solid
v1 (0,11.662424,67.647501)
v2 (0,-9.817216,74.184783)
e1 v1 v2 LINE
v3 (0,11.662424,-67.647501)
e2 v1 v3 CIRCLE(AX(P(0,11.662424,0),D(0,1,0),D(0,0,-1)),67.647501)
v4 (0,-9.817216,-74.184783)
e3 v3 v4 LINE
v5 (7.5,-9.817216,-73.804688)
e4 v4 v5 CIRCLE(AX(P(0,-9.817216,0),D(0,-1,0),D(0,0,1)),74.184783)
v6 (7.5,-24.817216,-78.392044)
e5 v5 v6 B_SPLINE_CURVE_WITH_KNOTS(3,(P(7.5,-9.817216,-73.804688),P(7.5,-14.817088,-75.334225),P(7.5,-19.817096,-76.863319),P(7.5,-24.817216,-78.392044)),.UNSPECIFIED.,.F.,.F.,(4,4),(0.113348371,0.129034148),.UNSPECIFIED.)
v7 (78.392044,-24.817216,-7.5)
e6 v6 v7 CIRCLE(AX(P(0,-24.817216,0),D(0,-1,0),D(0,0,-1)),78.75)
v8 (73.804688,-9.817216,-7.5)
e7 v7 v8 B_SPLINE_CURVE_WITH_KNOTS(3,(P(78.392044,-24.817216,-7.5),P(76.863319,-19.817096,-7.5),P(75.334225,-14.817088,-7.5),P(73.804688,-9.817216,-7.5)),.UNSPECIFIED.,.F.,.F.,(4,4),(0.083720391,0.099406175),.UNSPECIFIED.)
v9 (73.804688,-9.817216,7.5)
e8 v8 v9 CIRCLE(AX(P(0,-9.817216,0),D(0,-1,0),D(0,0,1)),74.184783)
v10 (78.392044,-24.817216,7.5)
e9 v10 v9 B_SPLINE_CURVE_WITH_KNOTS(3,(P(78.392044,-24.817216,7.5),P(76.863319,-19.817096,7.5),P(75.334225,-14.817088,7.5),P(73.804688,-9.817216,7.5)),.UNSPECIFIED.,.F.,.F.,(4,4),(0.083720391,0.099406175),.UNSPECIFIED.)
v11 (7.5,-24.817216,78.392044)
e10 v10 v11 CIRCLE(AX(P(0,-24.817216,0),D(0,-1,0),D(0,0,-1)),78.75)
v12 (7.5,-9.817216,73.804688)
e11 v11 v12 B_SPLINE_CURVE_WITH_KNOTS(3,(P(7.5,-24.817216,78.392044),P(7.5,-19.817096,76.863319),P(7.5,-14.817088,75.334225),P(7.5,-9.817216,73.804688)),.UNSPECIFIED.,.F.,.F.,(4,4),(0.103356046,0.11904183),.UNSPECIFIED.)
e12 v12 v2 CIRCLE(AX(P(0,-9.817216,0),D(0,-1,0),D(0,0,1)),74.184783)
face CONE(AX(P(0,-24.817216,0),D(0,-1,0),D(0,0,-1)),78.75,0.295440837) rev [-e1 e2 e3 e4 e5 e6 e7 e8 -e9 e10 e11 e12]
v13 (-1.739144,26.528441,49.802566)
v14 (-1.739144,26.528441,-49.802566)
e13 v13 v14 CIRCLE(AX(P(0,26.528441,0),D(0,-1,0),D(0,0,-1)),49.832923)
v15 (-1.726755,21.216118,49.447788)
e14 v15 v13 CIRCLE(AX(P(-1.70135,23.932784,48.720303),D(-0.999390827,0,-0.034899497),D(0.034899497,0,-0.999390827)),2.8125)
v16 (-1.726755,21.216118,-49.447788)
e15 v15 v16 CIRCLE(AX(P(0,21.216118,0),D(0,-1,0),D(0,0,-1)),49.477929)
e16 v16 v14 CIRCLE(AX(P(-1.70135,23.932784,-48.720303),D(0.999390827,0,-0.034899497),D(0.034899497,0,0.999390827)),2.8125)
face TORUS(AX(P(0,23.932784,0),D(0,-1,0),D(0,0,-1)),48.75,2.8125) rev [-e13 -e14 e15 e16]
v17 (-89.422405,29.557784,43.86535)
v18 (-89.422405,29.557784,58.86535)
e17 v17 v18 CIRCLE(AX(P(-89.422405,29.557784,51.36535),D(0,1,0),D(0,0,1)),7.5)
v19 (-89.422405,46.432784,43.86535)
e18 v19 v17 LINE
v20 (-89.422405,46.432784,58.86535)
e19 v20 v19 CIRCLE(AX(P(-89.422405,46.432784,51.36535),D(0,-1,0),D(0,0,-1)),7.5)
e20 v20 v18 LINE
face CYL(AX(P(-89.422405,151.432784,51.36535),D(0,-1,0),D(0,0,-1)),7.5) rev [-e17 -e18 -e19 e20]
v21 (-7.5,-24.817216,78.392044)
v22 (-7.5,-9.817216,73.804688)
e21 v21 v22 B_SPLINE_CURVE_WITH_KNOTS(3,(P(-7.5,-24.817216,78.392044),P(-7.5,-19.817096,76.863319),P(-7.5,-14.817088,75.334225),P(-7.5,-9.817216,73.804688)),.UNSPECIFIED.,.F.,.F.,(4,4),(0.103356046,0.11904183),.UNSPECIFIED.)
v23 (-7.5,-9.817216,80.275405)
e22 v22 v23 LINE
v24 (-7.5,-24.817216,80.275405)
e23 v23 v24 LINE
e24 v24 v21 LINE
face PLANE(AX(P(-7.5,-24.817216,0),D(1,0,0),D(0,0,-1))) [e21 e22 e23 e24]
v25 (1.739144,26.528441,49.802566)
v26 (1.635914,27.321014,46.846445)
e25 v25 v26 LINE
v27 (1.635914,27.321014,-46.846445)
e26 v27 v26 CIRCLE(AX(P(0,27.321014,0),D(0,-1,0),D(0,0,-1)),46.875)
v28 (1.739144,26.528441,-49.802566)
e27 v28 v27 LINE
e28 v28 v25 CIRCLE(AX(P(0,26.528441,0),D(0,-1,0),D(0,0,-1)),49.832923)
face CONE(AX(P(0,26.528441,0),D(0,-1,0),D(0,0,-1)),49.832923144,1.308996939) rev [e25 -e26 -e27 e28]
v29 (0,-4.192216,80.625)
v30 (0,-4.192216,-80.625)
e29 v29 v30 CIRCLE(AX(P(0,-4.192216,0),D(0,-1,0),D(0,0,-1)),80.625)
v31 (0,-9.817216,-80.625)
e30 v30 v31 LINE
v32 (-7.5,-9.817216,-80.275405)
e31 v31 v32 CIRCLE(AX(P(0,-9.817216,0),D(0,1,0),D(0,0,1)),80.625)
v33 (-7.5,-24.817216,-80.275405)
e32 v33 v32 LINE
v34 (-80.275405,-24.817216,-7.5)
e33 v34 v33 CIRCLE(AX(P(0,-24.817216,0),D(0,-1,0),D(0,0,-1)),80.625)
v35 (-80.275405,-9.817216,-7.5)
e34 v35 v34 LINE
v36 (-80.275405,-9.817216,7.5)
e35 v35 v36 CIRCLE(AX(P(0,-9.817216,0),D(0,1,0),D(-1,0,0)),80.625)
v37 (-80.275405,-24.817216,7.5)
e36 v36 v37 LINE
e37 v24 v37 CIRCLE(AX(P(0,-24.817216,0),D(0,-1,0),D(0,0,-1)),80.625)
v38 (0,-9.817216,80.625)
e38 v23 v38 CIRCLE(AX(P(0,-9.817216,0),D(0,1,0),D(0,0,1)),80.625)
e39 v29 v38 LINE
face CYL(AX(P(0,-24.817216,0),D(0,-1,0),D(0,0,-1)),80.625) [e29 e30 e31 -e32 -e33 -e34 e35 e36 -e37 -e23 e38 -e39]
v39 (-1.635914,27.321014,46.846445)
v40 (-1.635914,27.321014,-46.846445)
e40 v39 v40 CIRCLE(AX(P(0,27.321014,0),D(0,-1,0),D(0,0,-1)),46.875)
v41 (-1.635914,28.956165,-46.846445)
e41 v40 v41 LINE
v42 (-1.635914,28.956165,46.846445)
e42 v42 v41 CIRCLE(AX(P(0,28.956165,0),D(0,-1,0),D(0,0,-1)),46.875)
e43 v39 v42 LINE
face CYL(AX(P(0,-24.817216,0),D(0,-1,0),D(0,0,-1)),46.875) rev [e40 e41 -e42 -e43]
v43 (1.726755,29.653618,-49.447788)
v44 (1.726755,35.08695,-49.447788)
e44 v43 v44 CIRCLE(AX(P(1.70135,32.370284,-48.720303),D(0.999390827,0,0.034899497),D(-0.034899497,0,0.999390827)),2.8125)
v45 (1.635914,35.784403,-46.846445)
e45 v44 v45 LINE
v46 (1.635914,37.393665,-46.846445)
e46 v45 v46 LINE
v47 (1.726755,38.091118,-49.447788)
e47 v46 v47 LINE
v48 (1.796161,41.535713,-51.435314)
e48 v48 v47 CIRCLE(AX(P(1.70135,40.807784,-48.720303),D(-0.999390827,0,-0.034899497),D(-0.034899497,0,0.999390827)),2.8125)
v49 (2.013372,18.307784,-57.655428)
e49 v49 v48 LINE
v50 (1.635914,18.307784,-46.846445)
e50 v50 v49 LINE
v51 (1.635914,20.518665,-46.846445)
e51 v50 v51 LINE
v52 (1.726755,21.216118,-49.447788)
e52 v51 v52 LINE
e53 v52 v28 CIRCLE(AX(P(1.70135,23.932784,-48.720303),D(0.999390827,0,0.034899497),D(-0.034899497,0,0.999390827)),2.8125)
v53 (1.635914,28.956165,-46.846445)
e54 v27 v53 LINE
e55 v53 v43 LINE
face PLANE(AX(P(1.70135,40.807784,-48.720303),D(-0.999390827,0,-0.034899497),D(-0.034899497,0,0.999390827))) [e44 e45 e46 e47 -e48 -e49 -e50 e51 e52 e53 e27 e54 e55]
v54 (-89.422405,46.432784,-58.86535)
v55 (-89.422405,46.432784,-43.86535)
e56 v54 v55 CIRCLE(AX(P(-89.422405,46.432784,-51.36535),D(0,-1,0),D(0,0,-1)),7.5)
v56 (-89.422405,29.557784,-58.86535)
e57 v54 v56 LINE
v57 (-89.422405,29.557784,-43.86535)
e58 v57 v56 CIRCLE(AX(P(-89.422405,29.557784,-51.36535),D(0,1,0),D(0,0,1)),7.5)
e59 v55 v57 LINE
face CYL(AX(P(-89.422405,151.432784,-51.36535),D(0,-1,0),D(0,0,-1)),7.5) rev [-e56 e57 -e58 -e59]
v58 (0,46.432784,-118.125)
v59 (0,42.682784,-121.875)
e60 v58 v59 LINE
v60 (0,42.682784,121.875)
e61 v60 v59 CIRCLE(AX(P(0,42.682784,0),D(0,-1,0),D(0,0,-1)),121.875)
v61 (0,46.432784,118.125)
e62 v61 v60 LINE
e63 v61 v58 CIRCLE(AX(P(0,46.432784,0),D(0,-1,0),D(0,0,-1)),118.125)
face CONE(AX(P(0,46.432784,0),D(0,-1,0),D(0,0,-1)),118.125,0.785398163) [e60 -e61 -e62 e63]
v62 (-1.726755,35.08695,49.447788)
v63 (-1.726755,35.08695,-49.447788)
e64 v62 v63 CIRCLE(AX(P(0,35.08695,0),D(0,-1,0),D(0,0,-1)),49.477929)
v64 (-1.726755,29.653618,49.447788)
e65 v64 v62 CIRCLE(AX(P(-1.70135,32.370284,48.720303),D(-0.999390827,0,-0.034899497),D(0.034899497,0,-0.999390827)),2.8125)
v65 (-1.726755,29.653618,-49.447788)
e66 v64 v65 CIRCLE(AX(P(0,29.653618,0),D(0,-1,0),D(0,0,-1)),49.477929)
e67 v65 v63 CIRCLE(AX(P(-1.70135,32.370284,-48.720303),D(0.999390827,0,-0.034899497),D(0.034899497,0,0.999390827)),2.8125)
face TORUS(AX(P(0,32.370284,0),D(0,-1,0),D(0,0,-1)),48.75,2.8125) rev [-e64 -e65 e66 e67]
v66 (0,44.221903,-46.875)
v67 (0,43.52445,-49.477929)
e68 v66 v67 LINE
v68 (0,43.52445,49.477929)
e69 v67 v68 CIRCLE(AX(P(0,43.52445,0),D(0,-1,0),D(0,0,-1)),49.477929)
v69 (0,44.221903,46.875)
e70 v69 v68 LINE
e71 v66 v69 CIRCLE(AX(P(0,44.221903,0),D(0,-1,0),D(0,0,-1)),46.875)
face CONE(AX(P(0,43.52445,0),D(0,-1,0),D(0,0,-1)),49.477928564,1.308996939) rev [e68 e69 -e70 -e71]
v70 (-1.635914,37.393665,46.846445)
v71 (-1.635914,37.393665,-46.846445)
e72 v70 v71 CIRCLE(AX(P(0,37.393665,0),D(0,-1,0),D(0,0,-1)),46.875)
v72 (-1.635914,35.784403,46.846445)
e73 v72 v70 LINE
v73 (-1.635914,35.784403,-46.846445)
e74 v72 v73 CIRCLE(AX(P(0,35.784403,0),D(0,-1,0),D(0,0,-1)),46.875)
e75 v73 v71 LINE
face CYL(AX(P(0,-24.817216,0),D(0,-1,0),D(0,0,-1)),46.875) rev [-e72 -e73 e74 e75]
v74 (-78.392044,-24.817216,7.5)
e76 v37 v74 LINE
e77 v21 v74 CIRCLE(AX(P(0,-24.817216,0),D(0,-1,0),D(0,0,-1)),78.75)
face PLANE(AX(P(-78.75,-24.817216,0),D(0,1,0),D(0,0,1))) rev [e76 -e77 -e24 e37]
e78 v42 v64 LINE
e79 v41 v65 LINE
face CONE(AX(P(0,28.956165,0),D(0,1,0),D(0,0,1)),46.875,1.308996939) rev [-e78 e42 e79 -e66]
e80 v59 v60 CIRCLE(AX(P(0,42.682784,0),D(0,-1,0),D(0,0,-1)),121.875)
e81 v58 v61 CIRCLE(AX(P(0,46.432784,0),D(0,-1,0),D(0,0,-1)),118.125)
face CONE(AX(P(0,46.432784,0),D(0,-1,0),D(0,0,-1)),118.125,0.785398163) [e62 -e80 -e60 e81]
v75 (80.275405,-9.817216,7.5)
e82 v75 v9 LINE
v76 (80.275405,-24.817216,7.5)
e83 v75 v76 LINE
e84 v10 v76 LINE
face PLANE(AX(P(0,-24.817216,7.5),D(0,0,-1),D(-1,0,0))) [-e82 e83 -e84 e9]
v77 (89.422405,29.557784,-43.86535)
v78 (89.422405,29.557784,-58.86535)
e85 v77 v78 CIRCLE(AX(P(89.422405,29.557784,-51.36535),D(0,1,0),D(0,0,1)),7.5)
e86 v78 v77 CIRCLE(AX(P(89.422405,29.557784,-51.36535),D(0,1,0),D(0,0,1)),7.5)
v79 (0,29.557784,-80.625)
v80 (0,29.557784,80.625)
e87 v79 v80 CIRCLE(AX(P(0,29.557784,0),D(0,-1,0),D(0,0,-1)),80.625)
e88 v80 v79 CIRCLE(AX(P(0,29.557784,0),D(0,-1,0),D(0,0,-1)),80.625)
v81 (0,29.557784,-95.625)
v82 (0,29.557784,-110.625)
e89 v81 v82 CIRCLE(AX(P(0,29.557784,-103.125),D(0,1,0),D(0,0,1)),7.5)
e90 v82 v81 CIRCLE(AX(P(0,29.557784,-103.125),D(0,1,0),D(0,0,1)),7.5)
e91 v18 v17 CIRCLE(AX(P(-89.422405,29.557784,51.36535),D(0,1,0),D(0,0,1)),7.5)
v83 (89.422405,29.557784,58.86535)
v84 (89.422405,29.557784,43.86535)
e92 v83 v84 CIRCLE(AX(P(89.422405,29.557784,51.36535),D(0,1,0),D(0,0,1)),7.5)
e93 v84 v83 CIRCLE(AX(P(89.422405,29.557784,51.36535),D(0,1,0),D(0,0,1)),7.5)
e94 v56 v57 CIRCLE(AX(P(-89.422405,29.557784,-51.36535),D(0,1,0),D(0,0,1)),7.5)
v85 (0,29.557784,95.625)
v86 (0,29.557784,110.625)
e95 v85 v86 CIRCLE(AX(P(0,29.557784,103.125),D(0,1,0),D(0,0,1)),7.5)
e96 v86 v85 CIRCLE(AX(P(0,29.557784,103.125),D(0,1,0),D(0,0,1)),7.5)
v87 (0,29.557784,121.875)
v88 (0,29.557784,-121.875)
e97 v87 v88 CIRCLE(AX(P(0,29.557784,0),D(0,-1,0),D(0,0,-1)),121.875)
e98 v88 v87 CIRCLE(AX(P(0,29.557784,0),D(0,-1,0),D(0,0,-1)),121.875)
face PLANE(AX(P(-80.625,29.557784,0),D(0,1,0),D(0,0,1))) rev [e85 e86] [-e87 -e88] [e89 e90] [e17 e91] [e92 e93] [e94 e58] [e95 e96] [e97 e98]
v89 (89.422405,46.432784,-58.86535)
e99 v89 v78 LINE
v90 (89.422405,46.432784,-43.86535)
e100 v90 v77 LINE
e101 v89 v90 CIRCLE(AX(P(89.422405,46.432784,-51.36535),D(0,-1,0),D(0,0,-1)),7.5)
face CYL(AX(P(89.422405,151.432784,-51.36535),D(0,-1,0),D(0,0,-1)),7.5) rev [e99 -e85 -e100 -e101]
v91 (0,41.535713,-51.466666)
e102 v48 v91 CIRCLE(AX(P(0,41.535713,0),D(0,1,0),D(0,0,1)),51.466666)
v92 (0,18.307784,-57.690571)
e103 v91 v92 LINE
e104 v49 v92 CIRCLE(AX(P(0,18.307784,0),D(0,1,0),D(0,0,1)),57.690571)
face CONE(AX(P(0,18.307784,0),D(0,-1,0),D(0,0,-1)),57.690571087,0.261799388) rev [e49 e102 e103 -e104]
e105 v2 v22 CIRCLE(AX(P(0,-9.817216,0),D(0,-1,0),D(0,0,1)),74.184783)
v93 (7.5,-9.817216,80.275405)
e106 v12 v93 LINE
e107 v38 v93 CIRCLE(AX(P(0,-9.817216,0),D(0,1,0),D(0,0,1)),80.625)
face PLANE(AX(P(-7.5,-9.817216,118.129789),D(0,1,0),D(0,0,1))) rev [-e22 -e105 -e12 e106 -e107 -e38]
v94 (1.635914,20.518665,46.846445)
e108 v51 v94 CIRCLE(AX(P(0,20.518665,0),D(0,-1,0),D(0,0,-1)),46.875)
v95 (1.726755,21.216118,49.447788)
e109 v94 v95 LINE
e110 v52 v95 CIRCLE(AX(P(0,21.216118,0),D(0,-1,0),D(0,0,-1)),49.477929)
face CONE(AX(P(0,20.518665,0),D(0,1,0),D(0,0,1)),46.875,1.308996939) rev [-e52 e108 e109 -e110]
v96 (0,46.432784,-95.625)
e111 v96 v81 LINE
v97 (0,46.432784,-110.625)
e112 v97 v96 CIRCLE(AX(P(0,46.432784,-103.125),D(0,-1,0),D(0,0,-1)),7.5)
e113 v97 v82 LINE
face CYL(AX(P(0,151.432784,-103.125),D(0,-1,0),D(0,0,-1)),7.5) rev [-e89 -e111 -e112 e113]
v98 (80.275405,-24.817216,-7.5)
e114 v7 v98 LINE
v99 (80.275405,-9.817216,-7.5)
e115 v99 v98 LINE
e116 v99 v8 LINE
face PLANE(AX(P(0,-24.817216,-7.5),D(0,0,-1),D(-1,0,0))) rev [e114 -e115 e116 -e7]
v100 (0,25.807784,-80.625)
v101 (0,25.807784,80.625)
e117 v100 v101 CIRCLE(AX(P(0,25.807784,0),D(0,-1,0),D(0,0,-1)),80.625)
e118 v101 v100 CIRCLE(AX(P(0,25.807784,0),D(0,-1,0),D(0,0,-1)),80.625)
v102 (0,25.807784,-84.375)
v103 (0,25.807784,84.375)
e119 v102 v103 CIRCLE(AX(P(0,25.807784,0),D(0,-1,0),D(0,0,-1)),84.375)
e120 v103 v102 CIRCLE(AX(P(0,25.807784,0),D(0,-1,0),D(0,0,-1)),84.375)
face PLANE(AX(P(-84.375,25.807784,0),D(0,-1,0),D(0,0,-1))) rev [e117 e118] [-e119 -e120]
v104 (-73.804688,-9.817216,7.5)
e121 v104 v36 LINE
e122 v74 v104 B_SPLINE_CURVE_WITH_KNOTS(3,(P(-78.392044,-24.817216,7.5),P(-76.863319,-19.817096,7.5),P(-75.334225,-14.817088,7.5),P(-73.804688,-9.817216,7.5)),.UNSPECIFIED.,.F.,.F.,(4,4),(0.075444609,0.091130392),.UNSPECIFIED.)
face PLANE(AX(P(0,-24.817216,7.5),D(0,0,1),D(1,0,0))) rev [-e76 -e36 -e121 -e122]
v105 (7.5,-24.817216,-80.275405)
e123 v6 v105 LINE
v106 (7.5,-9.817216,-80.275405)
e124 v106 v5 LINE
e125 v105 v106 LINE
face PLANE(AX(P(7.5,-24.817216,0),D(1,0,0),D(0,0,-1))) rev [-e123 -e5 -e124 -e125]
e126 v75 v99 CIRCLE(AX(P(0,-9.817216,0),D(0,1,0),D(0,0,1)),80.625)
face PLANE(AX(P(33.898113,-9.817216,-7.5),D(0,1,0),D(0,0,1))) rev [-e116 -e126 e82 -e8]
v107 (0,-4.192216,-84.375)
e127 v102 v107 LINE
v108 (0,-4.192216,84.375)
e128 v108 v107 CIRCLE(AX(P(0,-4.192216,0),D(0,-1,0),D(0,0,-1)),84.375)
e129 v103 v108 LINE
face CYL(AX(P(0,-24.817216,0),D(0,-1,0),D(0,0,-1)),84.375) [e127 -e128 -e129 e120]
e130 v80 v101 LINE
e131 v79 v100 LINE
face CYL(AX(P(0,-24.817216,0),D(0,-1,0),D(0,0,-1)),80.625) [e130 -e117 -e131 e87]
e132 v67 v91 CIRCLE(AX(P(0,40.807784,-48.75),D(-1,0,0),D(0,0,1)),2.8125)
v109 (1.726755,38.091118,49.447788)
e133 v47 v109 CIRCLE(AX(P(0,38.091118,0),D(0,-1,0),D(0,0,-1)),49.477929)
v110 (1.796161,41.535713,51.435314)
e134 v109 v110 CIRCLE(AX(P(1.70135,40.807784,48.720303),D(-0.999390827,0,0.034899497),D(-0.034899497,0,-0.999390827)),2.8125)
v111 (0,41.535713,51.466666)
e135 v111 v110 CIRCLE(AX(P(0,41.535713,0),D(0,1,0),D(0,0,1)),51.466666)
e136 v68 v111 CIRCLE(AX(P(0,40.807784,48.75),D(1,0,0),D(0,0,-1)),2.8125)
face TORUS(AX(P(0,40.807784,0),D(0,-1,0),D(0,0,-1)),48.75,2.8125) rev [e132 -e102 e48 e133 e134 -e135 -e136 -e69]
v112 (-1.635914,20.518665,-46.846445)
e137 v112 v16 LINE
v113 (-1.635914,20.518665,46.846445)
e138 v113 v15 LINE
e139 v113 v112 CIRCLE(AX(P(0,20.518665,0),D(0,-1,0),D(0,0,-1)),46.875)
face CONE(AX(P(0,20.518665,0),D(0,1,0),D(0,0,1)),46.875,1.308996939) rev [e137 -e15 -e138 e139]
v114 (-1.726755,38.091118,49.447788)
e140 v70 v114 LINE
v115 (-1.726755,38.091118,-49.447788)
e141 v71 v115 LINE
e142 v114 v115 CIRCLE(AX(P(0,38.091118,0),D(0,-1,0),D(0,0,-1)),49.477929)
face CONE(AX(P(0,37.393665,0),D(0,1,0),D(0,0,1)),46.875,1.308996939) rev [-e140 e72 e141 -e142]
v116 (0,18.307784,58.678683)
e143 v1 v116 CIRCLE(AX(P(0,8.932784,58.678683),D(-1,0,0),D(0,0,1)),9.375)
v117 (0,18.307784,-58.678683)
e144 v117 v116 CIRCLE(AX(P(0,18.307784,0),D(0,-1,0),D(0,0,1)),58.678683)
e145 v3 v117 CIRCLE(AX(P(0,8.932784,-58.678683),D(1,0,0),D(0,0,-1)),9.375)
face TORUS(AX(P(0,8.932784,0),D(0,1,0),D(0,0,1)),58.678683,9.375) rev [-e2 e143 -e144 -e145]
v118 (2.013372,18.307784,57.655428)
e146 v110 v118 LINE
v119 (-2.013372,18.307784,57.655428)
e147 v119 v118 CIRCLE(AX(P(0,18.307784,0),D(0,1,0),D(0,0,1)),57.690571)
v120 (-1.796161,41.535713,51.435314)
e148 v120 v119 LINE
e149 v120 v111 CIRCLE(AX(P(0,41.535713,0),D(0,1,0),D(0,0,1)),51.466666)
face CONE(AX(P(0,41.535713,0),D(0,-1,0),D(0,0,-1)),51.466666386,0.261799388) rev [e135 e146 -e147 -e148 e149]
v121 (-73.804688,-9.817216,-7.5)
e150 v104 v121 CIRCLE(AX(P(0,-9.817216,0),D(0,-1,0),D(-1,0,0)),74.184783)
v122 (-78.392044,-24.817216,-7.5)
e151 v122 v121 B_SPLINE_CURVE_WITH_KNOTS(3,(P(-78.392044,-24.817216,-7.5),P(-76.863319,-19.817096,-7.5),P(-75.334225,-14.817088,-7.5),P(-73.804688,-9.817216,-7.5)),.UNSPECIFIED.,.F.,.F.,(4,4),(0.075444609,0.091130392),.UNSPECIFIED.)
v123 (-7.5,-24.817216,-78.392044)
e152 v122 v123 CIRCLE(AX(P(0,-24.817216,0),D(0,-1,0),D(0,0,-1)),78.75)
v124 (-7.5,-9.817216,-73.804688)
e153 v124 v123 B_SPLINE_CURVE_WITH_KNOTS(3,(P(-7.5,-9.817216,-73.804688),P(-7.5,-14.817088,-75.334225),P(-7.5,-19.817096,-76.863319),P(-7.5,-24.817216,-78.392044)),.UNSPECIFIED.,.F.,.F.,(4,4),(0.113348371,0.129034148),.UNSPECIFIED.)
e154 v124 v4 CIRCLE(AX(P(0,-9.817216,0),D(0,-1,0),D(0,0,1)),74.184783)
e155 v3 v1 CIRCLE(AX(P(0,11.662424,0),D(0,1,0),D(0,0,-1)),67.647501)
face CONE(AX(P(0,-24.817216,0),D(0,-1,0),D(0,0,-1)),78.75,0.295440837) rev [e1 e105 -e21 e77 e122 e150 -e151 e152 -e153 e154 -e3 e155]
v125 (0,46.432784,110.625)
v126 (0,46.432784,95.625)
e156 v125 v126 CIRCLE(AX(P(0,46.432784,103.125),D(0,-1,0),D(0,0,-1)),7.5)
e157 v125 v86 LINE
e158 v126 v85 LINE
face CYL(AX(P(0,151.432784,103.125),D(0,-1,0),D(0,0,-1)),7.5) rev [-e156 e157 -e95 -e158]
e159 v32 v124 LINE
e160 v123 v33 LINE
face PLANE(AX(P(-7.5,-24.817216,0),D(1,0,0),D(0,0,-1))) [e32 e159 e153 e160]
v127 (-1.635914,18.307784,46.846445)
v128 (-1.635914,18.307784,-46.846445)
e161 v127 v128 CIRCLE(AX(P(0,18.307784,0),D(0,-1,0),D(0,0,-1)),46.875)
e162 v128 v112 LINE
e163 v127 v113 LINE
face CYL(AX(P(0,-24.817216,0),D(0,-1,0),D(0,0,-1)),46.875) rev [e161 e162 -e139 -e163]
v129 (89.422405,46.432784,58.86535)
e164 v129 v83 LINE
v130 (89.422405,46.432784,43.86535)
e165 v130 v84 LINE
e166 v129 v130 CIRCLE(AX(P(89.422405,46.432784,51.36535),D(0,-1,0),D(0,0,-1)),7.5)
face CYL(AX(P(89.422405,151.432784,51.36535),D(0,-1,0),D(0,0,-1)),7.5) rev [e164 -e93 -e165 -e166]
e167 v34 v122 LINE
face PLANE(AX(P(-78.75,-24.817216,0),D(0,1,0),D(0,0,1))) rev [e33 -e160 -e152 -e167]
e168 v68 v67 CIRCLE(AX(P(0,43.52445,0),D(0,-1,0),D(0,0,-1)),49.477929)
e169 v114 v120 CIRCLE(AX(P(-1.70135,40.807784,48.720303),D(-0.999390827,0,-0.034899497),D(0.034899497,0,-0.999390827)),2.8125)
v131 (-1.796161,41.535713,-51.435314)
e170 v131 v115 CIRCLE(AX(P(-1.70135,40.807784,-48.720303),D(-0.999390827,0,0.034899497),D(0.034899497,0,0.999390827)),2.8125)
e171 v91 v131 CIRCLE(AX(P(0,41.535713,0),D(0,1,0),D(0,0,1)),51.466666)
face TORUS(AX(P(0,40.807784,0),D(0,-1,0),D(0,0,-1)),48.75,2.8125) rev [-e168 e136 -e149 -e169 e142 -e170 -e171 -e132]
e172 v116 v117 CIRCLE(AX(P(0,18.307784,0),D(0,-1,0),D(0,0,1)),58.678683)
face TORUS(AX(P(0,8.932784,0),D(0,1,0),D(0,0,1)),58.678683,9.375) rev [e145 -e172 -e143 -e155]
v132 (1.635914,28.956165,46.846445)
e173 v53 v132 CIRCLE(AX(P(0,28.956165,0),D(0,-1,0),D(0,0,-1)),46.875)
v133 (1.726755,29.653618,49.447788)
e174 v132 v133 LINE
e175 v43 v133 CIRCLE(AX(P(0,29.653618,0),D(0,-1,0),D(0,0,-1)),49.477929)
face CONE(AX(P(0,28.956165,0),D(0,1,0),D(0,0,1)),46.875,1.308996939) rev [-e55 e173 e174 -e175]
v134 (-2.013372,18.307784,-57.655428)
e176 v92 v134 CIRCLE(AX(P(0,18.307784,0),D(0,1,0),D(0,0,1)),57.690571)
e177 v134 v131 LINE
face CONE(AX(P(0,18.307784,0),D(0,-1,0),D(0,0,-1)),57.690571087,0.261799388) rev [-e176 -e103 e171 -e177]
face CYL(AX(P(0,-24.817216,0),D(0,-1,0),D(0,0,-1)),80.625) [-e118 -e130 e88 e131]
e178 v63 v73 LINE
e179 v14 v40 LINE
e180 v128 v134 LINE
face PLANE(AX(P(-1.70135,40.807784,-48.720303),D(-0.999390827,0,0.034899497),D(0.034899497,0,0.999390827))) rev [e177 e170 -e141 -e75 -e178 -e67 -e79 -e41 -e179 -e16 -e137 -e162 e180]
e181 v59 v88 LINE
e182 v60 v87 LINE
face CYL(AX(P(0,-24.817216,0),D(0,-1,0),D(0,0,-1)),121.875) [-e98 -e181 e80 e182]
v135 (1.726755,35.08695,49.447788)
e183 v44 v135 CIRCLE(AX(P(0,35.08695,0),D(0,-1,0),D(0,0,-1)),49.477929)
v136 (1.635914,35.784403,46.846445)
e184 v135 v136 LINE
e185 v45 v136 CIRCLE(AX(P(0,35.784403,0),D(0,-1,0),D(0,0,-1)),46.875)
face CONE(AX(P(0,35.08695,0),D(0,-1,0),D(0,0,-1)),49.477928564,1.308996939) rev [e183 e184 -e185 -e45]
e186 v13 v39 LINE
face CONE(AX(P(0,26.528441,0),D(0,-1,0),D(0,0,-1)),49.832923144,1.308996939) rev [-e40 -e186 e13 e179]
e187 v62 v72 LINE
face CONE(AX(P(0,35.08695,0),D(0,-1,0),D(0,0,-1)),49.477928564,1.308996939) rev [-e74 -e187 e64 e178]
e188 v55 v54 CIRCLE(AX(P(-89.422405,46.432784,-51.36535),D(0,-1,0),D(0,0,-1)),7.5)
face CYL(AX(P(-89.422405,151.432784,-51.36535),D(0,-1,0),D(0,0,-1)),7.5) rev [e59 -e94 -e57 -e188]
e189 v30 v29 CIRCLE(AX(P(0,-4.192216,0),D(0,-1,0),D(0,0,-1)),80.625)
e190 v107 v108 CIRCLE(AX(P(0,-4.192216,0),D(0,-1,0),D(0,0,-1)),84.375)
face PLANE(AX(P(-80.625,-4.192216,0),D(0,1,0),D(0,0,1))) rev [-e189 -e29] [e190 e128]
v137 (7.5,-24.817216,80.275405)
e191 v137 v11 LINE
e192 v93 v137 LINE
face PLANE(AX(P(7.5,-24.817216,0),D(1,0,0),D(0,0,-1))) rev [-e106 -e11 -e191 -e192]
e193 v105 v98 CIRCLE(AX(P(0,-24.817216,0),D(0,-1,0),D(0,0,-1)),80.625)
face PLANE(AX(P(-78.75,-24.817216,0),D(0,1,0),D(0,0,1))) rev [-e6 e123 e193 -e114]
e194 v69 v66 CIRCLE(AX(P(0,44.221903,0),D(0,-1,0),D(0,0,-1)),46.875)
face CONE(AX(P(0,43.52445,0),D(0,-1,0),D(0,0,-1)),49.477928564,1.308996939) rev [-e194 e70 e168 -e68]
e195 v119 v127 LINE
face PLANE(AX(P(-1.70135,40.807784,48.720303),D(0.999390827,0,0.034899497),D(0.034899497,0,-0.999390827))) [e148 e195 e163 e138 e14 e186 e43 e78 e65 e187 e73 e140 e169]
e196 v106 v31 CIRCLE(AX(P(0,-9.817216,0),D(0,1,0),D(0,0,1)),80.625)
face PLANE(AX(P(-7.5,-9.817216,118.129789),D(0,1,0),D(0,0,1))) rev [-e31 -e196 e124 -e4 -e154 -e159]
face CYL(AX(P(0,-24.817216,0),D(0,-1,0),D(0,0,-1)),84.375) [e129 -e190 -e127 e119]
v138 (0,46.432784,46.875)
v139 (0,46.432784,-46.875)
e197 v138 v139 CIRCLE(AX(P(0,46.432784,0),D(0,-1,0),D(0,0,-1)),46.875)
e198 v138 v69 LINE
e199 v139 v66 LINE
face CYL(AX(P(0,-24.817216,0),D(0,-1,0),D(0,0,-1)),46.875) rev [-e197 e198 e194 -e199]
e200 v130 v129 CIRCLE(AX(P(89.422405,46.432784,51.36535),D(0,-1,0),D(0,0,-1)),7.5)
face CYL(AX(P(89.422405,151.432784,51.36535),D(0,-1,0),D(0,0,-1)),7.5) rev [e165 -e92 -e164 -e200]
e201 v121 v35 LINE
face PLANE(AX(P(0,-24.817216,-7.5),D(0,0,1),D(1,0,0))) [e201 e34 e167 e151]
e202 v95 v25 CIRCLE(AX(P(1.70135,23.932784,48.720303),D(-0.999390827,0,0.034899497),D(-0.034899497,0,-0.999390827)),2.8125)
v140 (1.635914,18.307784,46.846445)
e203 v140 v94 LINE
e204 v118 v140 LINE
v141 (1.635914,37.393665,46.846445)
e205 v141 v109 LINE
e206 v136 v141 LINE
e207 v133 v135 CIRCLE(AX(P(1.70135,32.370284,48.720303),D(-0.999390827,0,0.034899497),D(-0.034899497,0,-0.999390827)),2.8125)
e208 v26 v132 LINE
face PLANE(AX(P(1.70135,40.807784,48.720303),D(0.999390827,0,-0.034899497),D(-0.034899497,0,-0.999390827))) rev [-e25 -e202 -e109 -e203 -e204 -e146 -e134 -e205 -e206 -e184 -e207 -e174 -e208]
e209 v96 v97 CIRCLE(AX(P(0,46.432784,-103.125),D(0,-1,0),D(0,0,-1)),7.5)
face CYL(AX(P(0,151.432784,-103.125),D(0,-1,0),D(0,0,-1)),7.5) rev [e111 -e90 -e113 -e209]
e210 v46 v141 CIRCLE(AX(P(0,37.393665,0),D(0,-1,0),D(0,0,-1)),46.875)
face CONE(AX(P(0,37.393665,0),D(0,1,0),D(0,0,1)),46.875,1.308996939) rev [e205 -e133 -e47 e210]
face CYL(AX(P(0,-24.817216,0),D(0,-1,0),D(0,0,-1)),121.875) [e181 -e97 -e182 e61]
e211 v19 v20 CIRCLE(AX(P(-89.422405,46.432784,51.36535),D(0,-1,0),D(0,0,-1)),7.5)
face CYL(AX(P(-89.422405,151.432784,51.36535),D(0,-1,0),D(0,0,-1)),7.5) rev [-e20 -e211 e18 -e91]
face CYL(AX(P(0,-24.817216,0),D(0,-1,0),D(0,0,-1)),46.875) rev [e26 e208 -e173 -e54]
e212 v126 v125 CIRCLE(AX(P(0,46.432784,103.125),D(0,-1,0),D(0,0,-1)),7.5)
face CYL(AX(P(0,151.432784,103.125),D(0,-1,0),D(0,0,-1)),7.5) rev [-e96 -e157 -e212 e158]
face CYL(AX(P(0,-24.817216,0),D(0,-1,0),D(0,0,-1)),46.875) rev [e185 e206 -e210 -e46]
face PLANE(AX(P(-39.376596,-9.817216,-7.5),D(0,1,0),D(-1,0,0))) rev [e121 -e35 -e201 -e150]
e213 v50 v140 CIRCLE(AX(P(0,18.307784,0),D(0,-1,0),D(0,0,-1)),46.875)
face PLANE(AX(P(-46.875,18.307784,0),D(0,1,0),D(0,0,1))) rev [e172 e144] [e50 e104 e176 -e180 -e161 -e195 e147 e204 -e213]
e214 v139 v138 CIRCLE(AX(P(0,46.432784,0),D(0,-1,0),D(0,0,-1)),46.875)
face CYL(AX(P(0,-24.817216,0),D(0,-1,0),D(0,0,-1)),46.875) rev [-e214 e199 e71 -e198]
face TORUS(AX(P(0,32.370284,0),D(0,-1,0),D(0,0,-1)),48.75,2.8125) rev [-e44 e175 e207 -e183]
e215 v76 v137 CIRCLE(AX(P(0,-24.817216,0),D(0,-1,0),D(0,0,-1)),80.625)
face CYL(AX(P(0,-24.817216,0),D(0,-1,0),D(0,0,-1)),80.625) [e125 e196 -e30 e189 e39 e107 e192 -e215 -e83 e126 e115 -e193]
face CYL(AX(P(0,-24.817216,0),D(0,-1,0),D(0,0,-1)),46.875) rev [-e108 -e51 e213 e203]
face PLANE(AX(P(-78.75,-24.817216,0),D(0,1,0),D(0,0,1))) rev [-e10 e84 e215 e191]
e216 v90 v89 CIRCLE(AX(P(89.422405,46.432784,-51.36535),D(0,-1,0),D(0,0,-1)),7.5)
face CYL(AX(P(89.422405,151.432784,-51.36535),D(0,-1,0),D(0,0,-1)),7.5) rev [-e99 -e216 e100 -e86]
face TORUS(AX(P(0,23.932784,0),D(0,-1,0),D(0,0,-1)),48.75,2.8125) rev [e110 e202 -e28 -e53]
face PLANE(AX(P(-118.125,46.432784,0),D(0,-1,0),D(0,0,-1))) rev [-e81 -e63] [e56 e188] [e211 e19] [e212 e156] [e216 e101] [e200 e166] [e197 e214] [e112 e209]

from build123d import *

# Parameters (mm, degrees)
FILLET1_R          = 5
SKETCH2_W          = 46.38448916527463
SKETCH2_H          = 8
CUT_EXTRUDE1_DEPTH = 4
SKETCH3_W          = 119.06569659747659
SKETCH3_H          = 8
CUT_EXTRUDE2_DEPTH = 4
CUT_REVOLVE2_ANGLE = 4.000000000000009
SKETCH5_R          = 3.999999999999999
SKETCH5_R_2        = 4.000000000000001
SKETCH5_R_3        = 4.000000000000005
CUT_EXTRUDE3_DEPTH = 94
SCALE_1_SCALE      = 1.875


with BuildPart() as part:
    # Sketch1 → Revolve1 (revolve)
    with BuildSketch(Plane.XY, mode=Mode.PRIVATE) as revolve1_sk:
        with BuildLine():
            Line((-43, -1.2e-16), (-43, 11))
            Line((-43, 11), (-45.00000000000001, 10.999999999999998))
            Line((-45.00000000000001, 10.999999999999998), (-45.00000000000001, 26.999999999999996))
            Line((-45.00000000000001, 26.999999999999996), (-43, 26.999999999999996))
            Line((-43, 26.999999999999996), (-43, 28.999999999999996))
            Line((-43, 28.999999999999996), (-65, 28.99999999999999))
            Line((-65, 28.99999999999999), (-65, 36))
            Line((-65, 36), (-63, 38))
            Line((-63, 38), (-25, 38))
            Line((-25, 38), (-25, 36.82086346304624))
            Line((-25, 36.82086346304624), (-26.388228567653783, 36.44888873943359))
            ThreePointArc((-26.388228567653783, 36.44888873943359), (-27.5, 34.99999999999999), (-26.388228567653783, 33.55111126056639))
            Line((-26.388228567653783, 33.55111126056639), (-25, 33.17913653695374))
            Line((-25, 33.17913653695374), (-25, 32.32086346304623))
            Line((-25, 32.32086346304623), (-26.38822856765378, 31.948888739433585))
            ThreePointArc((-26.38822856765378, 31.948888739433585), (-27.499999999999986, 30.5), (-26.388228567653783, 29.051111260566397))
            Line((-26.388228567653783, 29.051111260566397), (-25, 28.679136536953745))
            Line((-25, 28.679136536953745), (-25, 27.807055903779258))
            Line((-25, 27.807055903779258), (-26.57755901026072, 27.384350240967457))
            ThreePointArc((-26.57755901026072, 27.384350240967457), (-27.496662016431728, 25.899985958133367), (-26.38822856765378, 24.551111260566397))
            Line((-26.38822856765378, 24.551111260566397), (-25, 24.179136536953752))
            Line((-25, 24.179136536953752), (-24.999999999999996, 23))
            Line((-24.999999999999996, 23), (-34.99999999999999, 23))
            Line((-34.99999999999999, 23), (-42, 0))
            Line((-42, 0), (-43, -1.2e-16))
        make_face()
    revolve(revolve1_sk.sketch.rotate(Axis((0, 0, 0), (0, 1, 0)), 270), axis=Axis((0, 0, 0), (0, 1, 0)))

    # Fillet1
    fillet1_edges = [part.edges().sort_by_distance(p)[0] for p in [
        (-1.206e-14, 23, 34.99999999999999),
    ]]
    fillet(fillet1_edges, radius=FILLET1_R)

    # Sketch2 → Cut-Extrude1 (cut, symmetric)
    with BuildSketch(Plane.XY):
        with Locations((41.27123839114988, 4)):
            Rectangle(SKETCH2_W, SKETCH2_H)
        Polygon((-21.00085139372669, -1.2e-16), (-54.05436532646177, -1.2e-16), (-54.05436532646177, 7.9999999999999964), (-21.00085139372669, 8), align=None)
    extrude(amount=CUT_EXTRUDE1_DEPTH, both=True, mode=Mode.SUBTRACT)

    # Sketch3 → Cut-Extrude2 (cut, symmetric)
    with BuildSketch(Plane(origin=(0, 0, 0), x_dir=(0, 0, -1), z_dir=(1, 0, 0))):
        with Locations((-3.469705882441801, 4)):
            Rectangle(SKETCH3_W, SKETCH3_H)
    extrude(amount=CUT_EXTRUDE2_DEPTH, both=True, mode=Mode.SUBTRACT)

    # Sketch4 → Cut-Revolve2 (revolve, symmetric, cut)
    with BuildSketch(Plane(origin=(0, 0, 0), x_dir=(0, 0, -1), z_dir=(1, 0, 0))) as cut_revolve2_sk:
        with BuildLine():
            Line((-27.4488887394336, 35.38822856765377), (-30.768304579788595, 23))
            Line((-30.768304579788595, 23), (-24.499999999999996, 23))
            Line((-24.499999999999996, 23), (-24.499999999999996, 34.99999999999999))
            ThreePointArc((-24.499999999999996, 34.99999999999999), (-26.195789288330076, 33.51283270793928), (-27.4488887394336, 35.38822856765377))
        make_face()
        with BuildLine():
            Line((30.768304579788595, 23), (24.499999999999996, 23))
            Line((24.499999999999996, 23), (24.499999999999996, 34.99999999999999))
            ThreePointArc((24.499999999999996, 34.99999999999999), (26.195789288330076, 33.51283270793928), (27.4488887394336, 35.38822856765377))
            Line((27.4488887394336, 35.38822856765377), (30.768304579788595, 23))
        make_face()
    revolve(axis=Axis((0, 0, 0), (0, -1, 0)), revolution_arc=CUT_REVOLVE2_ANGLE / 2, mode=Mode.SUBTRACT)
    revolve(cut_revolve2_sk.sketch, axis=Axis((0, 0, 0), (0, 1, 0)), revolution_arc=CUT_REVOLVE2_ANGLE / 2, mode=Mode.SUBTRACT)

    # Sketch5 → Cut-Extrude3 (cut)
    with BuildSketch(Plane.XZ):
        with Locations(Location((-47.69194914270065, 27.394853293457416, 0), (0, 0, 270))):
            Circle(SKETCH5_R)
        with Locations(Location((0, 55, 0), (0, 0, 270))):
            Circle(SKETCH5_R_2)
        with Locations(Location((47.69194914270066, 27.394853293457416, 0), (0, 0, 270))):
            Circle(SKETCH5_R_3)
        with Locations(Location((-47.69194914270065, -27.394853293457416, 0), (0, 0, 270))):
            Circle(SKETCH5_R)
        with Locations(Location((0, -55, 0), (0, 0, 270))):
            Circle(SKETCH5_R_2)
        with Locations(Location((47.69194914270066, -27.394853293457416, 0), (0, 0, 270))):
            Circle(SKETCH5_R_3)
    extrude(amount=-CUT_EXTRUDE3_DEPTH, mode=Mode.SUBTRACT)


with BuildPart() as part_1:
    # Scale 1: scaled about (0, 28.362532631, 0)
    add(part.part.scale(SCALE_1_SCALE).moved(Location((0, -24.817216052125, 0))))


solid = part_1.part
